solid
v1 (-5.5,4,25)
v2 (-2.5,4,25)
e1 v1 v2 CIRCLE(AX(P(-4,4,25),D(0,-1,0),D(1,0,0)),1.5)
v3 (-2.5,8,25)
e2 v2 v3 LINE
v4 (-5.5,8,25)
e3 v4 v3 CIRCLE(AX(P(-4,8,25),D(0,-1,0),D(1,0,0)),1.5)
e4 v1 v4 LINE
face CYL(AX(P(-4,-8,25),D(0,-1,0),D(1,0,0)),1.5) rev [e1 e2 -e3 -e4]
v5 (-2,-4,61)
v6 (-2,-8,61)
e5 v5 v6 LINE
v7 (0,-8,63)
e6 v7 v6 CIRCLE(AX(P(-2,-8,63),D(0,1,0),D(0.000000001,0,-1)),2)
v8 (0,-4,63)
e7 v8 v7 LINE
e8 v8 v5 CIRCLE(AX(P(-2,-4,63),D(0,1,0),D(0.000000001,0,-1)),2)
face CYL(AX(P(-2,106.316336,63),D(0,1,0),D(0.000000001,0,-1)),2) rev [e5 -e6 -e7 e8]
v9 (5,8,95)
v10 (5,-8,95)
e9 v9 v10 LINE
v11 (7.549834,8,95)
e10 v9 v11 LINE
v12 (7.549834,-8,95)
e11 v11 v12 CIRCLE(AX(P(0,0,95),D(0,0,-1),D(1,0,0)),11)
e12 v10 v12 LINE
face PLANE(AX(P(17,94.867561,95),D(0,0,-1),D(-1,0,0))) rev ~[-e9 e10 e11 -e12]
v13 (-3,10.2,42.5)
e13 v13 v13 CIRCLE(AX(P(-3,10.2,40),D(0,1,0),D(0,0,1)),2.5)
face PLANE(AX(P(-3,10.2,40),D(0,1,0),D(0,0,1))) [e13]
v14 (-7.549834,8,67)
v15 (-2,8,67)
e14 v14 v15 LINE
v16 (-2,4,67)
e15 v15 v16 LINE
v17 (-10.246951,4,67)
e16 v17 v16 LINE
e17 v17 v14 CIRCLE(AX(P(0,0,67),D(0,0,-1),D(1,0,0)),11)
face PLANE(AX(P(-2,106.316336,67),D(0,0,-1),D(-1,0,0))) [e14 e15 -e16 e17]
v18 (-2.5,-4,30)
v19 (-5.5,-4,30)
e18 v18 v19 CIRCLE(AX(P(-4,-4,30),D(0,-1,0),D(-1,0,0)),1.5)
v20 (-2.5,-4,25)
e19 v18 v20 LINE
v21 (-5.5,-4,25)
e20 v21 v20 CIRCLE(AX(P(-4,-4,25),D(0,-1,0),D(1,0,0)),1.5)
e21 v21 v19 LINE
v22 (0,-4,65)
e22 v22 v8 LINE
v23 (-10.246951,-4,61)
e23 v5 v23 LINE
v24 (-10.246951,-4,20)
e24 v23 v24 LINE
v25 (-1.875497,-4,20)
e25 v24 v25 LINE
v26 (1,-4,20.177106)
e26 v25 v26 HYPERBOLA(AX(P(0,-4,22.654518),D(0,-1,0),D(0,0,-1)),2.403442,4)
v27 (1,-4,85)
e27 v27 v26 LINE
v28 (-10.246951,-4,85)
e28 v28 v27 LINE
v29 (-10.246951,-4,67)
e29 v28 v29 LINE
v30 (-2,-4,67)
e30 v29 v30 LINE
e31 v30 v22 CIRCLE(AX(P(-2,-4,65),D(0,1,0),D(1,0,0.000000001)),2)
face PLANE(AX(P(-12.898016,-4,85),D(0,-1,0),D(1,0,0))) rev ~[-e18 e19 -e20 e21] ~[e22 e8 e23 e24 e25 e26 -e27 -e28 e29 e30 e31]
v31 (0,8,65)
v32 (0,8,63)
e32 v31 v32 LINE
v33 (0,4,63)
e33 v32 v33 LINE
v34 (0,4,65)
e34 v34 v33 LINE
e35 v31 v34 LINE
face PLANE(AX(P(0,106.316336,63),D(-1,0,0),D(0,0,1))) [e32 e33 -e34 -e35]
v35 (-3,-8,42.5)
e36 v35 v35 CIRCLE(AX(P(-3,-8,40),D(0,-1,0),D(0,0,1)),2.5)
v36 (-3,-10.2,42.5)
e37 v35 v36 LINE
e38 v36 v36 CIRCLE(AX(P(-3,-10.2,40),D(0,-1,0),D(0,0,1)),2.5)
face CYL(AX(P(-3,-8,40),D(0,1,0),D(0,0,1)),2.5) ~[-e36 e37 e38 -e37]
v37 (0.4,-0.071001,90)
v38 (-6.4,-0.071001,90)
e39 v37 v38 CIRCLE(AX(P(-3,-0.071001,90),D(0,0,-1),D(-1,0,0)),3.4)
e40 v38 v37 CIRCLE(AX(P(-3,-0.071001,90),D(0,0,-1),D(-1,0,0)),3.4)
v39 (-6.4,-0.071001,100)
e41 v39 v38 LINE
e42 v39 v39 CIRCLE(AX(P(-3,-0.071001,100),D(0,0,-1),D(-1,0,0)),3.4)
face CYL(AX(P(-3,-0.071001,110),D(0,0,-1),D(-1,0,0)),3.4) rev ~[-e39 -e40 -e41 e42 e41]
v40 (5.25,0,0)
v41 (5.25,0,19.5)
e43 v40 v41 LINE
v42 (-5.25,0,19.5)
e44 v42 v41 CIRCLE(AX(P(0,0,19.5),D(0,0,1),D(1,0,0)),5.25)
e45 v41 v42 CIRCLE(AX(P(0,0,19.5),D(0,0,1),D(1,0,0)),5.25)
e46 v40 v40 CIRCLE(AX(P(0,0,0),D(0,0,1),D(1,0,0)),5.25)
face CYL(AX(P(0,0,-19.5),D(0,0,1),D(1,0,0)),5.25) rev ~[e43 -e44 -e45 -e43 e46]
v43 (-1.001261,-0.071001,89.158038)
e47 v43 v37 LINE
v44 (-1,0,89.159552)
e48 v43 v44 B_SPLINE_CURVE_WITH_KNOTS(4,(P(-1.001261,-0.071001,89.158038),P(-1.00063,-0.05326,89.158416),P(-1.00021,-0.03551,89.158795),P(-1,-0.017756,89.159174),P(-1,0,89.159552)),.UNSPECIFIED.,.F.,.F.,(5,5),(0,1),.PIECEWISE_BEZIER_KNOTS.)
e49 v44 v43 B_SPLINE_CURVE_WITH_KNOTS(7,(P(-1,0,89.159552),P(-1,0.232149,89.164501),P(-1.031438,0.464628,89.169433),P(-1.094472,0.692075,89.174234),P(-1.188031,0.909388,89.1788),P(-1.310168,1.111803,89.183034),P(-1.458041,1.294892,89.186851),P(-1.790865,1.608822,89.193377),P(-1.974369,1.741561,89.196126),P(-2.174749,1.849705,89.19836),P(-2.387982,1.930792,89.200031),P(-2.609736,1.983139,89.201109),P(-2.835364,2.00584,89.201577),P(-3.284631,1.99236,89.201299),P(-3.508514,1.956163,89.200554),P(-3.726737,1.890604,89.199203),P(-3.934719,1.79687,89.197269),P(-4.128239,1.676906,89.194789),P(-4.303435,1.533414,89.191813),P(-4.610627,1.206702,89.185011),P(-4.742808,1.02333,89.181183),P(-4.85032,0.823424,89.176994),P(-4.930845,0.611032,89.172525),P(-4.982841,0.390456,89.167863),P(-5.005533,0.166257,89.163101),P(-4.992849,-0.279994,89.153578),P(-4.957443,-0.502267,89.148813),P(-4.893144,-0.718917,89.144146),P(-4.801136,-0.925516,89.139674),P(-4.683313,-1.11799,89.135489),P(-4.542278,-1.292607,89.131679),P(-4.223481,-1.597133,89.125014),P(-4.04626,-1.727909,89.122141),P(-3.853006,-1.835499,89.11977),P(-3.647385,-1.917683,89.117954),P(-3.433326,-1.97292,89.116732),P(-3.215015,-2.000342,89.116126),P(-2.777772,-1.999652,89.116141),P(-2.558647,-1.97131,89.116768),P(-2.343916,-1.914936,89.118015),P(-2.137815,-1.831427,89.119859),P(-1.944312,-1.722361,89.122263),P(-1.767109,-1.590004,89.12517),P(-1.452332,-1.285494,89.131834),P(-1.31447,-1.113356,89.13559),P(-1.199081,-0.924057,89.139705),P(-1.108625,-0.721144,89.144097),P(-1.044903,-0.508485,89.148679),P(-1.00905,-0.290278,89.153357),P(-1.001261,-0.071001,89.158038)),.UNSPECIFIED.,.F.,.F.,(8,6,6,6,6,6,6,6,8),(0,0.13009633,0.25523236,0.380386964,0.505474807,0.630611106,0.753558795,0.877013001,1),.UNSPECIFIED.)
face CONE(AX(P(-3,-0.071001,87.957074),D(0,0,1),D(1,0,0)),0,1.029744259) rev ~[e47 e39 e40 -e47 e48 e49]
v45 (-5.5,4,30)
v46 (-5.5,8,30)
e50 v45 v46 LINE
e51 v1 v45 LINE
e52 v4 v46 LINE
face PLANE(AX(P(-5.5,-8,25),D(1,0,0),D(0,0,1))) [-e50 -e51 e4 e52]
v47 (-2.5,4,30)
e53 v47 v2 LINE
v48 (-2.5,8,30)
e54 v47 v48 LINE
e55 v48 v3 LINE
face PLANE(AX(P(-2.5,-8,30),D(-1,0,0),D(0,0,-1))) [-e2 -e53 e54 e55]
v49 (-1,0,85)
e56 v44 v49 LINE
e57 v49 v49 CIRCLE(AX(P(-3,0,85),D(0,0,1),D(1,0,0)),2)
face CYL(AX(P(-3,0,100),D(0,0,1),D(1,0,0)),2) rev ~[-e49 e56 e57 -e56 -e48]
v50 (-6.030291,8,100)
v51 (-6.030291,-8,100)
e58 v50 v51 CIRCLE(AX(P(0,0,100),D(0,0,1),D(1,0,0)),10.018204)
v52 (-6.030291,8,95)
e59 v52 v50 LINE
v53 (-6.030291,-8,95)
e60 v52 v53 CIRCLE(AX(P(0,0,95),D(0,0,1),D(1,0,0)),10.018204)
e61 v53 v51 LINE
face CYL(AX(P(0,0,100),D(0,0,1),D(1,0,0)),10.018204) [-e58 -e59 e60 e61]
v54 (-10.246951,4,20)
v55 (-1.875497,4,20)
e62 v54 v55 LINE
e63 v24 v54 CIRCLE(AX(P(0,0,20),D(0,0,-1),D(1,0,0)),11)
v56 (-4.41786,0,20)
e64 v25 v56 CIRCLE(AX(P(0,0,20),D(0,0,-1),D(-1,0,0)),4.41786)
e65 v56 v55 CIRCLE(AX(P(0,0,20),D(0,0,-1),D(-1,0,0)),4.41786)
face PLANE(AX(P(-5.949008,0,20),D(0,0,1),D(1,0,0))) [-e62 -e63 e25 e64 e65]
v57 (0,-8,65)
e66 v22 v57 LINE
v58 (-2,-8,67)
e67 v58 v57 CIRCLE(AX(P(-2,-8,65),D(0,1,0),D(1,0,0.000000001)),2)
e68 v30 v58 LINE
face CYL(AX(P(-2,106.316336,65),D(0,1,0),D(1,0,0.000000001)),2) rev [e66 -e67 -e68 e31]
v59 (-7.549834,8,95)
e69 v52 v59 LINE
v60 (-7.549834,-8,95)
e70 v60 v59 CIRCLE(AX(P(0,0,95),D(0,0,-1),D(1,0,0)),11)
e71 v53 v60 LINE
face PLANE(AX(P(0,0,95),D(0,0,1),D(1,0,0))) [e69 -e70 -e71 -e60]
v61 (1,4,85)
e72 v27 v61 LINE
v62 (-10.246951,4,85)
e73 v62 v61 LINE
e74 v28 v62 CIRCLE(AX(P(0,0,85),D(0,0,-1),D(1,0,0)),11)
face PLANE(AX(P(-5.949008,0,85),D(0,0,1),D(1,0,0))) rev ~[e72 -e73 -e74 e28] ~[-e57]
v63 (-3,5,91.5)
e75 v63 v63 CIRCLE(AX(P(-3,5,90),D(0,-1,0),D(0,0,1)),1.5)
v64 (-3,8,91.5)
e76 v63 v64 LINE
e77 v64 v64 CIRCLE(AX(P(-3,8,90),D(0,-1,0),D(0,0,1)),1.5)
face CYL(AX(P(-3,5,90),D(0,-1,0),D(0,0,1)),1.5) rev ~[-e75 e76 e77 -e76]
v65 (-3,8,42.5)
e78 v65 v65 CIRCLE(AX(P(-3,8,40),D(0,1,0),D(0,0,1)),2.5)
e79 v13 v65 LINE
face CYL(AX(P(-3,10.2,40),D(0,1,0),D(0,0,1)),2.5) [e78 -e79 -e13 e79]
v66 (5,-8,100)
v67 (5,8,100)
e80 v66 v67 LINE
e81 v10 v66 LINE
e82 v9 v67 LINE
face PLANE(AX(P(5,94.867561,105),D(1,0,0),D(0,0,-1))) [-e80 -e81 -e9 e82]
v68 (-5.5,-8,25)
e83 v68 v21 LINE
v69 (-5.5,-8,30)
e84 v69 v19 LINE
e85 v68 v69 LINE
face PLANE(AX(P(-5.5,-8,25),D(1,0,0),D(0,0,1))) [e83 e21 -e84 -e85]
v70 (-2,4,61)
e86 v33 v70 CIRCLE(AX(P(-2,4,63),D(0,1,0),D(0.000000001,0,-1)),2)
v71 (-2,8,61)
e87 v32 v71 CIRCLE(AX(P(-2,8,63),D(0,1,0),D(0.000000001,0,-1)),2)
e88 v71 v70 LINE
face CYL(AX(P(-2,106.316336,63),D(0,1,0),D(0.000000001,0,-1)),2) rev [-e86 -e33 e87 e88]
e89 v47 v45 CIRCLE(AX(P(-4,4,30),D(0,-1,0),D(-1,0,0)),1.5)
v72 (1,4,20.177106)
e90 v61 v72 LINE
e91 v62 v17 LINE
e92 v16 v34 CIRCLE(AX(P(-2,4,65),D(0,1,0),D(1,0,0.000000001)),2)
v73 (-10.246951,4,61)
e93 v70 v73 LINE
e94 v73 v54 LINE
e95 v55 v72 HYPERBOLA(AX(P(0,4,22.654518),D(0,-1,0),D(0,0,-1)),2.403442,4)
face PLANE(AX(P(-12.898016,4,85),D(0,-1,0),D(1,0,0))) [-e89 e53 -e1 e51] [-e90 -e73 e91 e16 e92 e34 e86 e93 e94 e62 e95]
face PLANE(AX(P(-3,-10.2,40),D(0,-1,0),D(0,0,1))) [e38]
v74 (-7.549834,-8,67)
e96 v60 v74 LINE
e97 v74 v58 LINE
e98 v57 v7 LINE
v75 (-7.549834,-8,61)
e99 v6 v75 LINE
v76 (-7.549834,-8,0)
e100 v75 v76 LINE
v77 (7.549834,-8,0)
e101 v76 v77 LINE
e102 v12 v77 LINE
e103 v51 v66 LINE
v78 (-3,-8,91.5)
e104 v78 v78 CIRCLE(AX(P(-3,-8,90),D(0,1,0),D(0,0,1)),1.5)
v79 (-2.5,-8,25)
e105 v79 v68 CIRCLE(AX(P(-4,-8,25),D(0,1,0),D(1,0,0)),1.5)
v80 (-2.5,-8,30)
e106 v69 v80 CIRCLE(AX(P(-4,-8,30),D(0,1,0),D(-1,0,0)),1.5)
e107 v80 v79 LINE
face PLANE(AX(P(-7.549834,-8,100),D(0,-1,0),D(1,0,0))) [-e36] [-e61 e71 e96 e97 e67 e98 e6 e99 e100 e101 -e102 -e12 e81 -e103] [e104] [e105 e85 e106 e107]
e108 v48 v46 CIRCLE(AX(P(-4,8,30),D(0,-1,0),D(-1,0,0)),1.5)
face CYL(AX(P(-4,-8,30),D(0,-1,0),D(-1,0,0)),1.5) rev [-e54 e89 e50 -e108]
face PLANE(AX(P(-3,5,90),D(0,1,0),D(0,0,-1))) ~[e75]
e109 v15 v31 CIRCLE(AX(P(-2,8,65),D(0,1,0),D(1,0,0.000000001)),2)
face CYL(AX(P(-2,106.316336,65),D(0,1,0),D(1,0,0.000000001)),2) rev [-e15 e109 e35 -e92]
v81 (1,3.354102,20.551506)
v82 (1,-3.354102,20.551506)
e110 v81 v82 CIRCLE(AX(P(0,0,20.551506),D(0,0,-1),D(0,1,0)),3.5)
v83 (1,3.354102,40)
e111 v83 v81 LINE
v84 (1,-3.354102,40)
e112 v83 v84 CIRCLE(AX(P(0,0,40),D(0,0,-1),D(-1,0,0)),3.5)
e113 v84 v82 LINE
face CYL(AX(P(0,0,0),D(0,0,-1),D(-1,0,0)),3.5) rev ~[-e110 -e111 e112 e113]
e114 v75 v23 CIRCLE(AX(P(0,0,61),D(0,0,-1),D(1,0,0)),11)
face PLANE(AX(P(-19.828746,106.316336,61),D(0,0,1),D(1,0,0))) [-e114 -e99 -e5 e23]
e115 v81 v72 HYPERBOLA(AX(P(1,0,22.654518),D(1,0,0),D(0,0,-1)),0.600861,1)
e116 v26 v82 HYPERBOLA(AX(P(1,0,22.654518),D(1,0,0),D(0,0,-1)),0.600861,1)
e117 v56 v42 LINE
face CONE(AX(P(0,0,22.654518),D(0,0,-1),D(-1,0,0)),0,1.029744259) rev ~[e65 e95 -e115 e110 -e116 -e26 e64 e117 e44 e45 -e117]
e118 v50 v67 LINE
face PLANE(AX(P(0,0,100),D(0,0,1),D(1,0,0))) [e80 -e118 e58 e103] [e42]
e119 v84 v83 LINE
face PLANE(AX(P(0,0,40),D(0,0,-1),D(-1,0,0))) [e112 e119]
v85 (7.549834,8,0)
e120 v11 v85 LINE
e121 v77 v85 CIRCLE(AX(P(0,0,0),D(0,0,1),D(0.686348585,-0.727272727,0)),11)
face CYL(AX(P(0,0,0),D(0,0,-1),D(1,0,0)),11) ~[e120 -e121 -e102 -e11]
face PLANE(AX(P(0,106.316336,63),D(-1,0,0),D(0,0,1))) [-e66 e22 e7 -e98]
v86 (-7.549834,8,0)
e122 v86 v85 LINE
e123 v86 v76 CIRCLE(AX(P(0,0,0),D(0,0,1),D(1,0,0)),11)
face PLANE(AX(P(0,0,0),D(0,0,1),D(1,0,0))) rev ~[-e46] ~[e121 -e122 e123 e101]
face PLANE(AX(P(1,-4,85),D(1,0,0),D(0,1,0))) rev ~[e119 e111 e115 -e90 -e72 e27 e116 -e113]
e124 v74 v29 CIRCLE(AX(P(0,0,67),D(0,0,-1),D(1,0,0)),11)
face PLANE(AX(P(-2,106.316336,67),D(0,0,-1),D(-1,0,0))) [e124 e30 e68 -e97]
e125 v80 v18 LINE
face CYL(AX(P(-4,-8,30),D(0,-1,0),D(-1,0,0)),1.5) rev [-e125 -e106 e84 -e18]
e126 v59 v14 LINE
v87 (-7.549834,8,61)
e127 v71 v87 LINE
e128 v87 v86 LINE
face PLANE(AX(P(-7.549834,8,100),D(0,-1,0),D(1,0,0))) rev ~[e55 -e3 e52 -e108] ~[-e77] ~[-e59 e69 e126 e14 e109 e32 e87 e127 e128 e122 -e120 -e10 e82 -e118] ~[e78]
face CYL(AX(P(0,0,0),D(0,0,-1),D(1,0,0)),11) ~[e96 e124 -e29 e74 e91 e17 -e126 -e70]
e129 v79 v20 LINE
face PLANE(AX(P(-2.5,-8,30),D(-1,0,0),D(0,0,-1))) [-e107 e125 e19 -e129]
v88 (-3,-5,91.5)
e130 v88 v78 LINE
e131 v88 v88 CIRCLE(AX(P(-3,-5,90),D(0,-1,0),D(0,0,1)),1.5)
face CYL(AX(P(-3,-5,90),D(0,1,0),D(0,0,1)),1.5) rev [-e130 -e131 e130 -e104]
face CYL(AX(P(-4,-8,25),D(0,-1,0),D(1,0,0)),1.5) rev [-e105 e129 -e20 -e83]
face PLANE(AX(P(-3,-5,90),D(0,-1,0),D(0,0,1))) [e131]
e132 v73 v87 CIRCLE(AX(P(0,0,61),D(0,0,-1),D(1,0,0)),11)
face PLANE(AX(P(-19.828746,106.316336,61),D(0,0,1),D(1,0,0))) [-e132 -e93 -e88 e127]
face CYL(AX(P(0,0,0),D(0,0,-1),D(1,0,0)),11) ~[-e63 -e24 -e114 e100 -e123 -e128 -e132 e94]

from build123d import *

# Parameters (mm, degrees)
SKETCH1_R                  = 11
BOSS_EXTRUDE1_DEPTH        = 100
CUT_EXTRUDE1_DEPTH         = 102.202766761
SKETCH3_R                  = 2
CUT_EXTRUDE2_DEPTH         = 60
CUT_EXTRUDE3_START         = -15
SKETCH4_W                  = 13.898015679
SKETCH4_H                  = 8
CUT_EXTRUDE3_DEPTH         = 65
CUT_EXTRUDE4_DEPTH         = 102.867561078
CUT_EXTRUDE4_DEPTH_BACK    = 102.867561078
SKETCH5_W                  = 12
SKETCH5_H                  = 10
M8_TAPPED_HOLE1_D          = 6.8
M8_TAPPED_HOLE1_DEPTH      = 10
M8_TAPPED_HOLE1_TIP        = 2.042926105
CUT_EXTRUDE5_START         = -3
SKETCH8_R                  = 1.5
CUT_EXTRUDE5_DEPTH         = 105.867561078
CUT_EXTRUDE6_DEPTH         = 102.867561078
CUT_EXTRUDE7_DEPTH         = 102.316336294
CUT_EXTRUDE7_DEPTH_BACK    = 102.316336294
M12X1_5_TAPPED_HOLE1_D     = 10.5
M12X1_5_TAPPED_HOLE1_DEPTH = 19.5
M12X1_5_TAPPED_HOLE1_TIP   = 3.15451825
SKETCH12_R                 = 2.5
BOSS_EXTRUDE2_DEPTH        = 2.2
BOSS_EXTRUDE3_START        = 2.2
SKETCH13_R                 = 2.5
BOSS_EXTRUDE3_DEPTH        = 2.2
SKETCH14_R                 = 3.5
CUT_EXTRUDE8_DEPTH         = 40
SKETCH15_R                 = 14.729549922
SKETCH15_R_2               = 10.018203868
CUT_EXTRUDE9_DEPTH         = 5


with BuildPart() as part:
    # Sketch1 → Boss-Extrude1 (new body)
    with BuildSketch(Plane.XY):
        Circle(SKETCH1_R)
    extrude(amount=BOSS_EXTRUDE1_DEPTH)

    # Sketch2 → Cut-Extrude1 (cut, through all)
    with BuildSketch(Plane.XY.offset(100)):
        with BuildLine():
            Line((-7.549834435, 8), (7.549834435, 8))
            ThreePointArc((7.549834435, 8), (0, 11), (-7.549834435, 8))
        make_face()
        with BuildLine():
            Line((-7.549834435, -8), (7.549834435, -8))
            ThreePointArc((7.549834435, -8), (0, -11), (-7.549834435, -8))
        make_face()
    extrude(amount=-CUT_EXTRUDE1_DEPTH, mode=Mode.SUBTRACT)

    # Sketch3 → Cut-Extrude2 (cut)
    with BuildSketch(Plane.XY.offset(100)):
        with Locations((-3, 0)):
            Circle(SKETCH3_R)
    extrude(amount=-CUT_EXTRUDE2_DEPTH, mode=Mode.SUBTRACT)

    # Sketch4 → Cut-Extrude3 (cut)
    with BuildSketch(Plane.XY.offset(100).offset(CUT_EXTRUDE3_START)):
        with Locations((-5.94900784, 0)):
            Rectangle(SKETCH4_W, SKETCH4_H)
    extrude(amount=-CUT_EXTRUDE3_DEPTH, mode=Mode.SUBTRACT)

    # Sketch5 → Cut-Extrude4 (cut, two sides: drawn at the far end of the back side and taken through both)
    with BuildSketch(Plane(origin=(0, -8, 0), x_dir=(-1, 0, 0), z_dir=(0, -1, 0)).offset(-CUT_EXTRUDE4_DEPTH_BACK)):
        with Locations((-11, -100)):
            Rectangle(SKETCH5_W, SKETCH5_H)
    extrude(amount=CUT_EXTRUDE4_DEPTH + CUT_EXTRUDE4_DEPTH_BACK, mode=Mode.SUBTRACT)

    # M8 Tapped Hole1
    with Locations(Plane(origin=(-3, -0.07100101, 100), x_dir=(1, 0, 0), z_dir=(0, 0, 1))):
        with Locations((0, 0)):
            Hole(M8_TAPPED_HOLE1_D / 2, depth=M8_TAPPED_HOLE1_DEPTH)
            with Locations((0, 0, -(M8_TAPPED_HOLE1_DEPTH + M8_TAPPED_HOLE1_TIP / 2))):  # 118° drill point
                Cone(0, M8_TAPPED_HOLE1_D / 2, M8_TAPPED_HOLE1_TIP, mode=Mode.SUBTRACT)

    # Sketch8 → Cut-Extrude5 (cut)
    with BuildSketch(Plane(origin=(0, -8, 0), x_dir=(-1, 0, 0), z_dir=(0, -1, 0)).offset(CUT_EXTRUDE5_START)):
        with Locations(Location((3, -90, 0), (0, 0, 270))):
            Circle(SKETCH8_R)
    cut_extrude5 = extrude(amount=CUT_EXTRUDE5_DEPTH, mode=Mode.SUBTRACT)

    # Mirror3: Cut-Extrude5 across plane
    add(cut_extrude5.mirror(Plane.ZX), mode=Mode.SUBTRACT)

    # Sketch9 → Cut-Extrude6 (cut, through all)
    with BuildSketch(Plane(origin=(0, -8, 0), x_dir=(-1, 0, 0), z_dir=(0, -1, 0))):
        with BuildLine():
            Line((2.5, -30), (2.5, -25))
            ThreePointArc((2.5, -25), (4, -23.5), (5.5, -25))
            Line((5.5, -25), (5.5, -30))
            ThreePointArc((5.5, -30), (4, -31.5), (2.5, -30))
        make_face()
    extrude(amount=-CUT_EXTRUDE6_DEPTH, mode=Mode.SUBTRACT)

    # Sketch10 → Cut-Extrude7 (cut, two sides: drawn at the far end of the back side and taken through both)
    with BuildSketch(Plane(origin=(0, 4, 0), x_dir=(-1, 0, 0), z_dir=(0, -1, 0)).offset(-CUT_EXTRUDE7_DEPTH_BACK)):
        with BuildLine():
            Line((2, -67), (19.82874578, -67))
            Line((19.82874578, -67), (19.82874578, -61))
            Line((19.82874578, -61), (2, -61))
            ThreePointArc((2, -61), (0.585786438, -61.585786438), (0, -63))
            Line((0, -63), (0, -65))
            ThreePointArc((0, -65), (0.585786438, -66.414213562), (2, -67))
        make_face()
    extrude(amount=CUT_EXTRUDE7_DEPTH + CUT_EXTRUDE7_DEPTH_BACK, mode=Mode.SUBTRACT)

    # M12x1.5 Tapped Hole1
    with Locations(Plane(origin=(0, 0, 0), x_dir=(-1, 0, 0), z_dir=(0, 0, -1))):
        with Locations((0, 0)):
            Hole(M12X1_5_TAPPED_HOLE1_D / 2, depth=M12X1_5_TAPPED_HOLE1_DEPTH)
            with Locations((0, 0, -(M12X1_5_TAPPED_HOLE1_DEPTH + M12X1_5_TAPPED_HOLE1_TIP / 2))):  # 118° drill point
                Cone(0, M12X1_5_TAPPED_HOLE1_D / 2, M12X1_5_TAPPED_HOLE1_TIP, mode=Mode.SUBTRACT)

    # Sketch12 → Boss-Extrude2 (add)
    with BuildSketch(Plane.XZ.offset(8)):
        with Locations(Location((-3, 40, 0), (0, 0, 90))):
            Circle(SKETCH12_R)
    extrude(amount=BOSS_EXTRUDE2_DEPTH)

    # Sketch13 → Boss-Extrude3 (add)
    with BuildSketch(Plane(origin=(0, 8, 0), x_dir=(1, 0, 0), z_dir=(0, 1, 0)).offset(BOSS_EXTRUDE3_START)):
        with Locations(Location((-3, -40, 0), (0, 0, 270))):
            Circle(SKETCH13_R)
    extrude(amount=-BOSS_EXTRUDE3_DEPTH)

    # Sketch14 → Cut-Extrude8 (cut)
    with BuildSketch(Plane(origin=(0, 0, 0), x_dir=(-1, 0, 0), z_dir=(0, 0, -1))):
        Circle(SKETCH14_R)
    extrude(amount=-CUT_EXTRUDE8_DEPTH, mode=Mode.SUBTRACT)

    # Sketch15 → Cut-Extrude9 (cut)
    with BuildSketch(Plane.XY.offset(100)):
        Circle(SKETCH15_R)
        Circle(SKETCH15_R_2, mode=Mode.SUBTRACT)
    extrude(amount=-CUT_EXTRUDE9_DEPTH, mode=Mode.SUBTRACT)


solid = part.part
